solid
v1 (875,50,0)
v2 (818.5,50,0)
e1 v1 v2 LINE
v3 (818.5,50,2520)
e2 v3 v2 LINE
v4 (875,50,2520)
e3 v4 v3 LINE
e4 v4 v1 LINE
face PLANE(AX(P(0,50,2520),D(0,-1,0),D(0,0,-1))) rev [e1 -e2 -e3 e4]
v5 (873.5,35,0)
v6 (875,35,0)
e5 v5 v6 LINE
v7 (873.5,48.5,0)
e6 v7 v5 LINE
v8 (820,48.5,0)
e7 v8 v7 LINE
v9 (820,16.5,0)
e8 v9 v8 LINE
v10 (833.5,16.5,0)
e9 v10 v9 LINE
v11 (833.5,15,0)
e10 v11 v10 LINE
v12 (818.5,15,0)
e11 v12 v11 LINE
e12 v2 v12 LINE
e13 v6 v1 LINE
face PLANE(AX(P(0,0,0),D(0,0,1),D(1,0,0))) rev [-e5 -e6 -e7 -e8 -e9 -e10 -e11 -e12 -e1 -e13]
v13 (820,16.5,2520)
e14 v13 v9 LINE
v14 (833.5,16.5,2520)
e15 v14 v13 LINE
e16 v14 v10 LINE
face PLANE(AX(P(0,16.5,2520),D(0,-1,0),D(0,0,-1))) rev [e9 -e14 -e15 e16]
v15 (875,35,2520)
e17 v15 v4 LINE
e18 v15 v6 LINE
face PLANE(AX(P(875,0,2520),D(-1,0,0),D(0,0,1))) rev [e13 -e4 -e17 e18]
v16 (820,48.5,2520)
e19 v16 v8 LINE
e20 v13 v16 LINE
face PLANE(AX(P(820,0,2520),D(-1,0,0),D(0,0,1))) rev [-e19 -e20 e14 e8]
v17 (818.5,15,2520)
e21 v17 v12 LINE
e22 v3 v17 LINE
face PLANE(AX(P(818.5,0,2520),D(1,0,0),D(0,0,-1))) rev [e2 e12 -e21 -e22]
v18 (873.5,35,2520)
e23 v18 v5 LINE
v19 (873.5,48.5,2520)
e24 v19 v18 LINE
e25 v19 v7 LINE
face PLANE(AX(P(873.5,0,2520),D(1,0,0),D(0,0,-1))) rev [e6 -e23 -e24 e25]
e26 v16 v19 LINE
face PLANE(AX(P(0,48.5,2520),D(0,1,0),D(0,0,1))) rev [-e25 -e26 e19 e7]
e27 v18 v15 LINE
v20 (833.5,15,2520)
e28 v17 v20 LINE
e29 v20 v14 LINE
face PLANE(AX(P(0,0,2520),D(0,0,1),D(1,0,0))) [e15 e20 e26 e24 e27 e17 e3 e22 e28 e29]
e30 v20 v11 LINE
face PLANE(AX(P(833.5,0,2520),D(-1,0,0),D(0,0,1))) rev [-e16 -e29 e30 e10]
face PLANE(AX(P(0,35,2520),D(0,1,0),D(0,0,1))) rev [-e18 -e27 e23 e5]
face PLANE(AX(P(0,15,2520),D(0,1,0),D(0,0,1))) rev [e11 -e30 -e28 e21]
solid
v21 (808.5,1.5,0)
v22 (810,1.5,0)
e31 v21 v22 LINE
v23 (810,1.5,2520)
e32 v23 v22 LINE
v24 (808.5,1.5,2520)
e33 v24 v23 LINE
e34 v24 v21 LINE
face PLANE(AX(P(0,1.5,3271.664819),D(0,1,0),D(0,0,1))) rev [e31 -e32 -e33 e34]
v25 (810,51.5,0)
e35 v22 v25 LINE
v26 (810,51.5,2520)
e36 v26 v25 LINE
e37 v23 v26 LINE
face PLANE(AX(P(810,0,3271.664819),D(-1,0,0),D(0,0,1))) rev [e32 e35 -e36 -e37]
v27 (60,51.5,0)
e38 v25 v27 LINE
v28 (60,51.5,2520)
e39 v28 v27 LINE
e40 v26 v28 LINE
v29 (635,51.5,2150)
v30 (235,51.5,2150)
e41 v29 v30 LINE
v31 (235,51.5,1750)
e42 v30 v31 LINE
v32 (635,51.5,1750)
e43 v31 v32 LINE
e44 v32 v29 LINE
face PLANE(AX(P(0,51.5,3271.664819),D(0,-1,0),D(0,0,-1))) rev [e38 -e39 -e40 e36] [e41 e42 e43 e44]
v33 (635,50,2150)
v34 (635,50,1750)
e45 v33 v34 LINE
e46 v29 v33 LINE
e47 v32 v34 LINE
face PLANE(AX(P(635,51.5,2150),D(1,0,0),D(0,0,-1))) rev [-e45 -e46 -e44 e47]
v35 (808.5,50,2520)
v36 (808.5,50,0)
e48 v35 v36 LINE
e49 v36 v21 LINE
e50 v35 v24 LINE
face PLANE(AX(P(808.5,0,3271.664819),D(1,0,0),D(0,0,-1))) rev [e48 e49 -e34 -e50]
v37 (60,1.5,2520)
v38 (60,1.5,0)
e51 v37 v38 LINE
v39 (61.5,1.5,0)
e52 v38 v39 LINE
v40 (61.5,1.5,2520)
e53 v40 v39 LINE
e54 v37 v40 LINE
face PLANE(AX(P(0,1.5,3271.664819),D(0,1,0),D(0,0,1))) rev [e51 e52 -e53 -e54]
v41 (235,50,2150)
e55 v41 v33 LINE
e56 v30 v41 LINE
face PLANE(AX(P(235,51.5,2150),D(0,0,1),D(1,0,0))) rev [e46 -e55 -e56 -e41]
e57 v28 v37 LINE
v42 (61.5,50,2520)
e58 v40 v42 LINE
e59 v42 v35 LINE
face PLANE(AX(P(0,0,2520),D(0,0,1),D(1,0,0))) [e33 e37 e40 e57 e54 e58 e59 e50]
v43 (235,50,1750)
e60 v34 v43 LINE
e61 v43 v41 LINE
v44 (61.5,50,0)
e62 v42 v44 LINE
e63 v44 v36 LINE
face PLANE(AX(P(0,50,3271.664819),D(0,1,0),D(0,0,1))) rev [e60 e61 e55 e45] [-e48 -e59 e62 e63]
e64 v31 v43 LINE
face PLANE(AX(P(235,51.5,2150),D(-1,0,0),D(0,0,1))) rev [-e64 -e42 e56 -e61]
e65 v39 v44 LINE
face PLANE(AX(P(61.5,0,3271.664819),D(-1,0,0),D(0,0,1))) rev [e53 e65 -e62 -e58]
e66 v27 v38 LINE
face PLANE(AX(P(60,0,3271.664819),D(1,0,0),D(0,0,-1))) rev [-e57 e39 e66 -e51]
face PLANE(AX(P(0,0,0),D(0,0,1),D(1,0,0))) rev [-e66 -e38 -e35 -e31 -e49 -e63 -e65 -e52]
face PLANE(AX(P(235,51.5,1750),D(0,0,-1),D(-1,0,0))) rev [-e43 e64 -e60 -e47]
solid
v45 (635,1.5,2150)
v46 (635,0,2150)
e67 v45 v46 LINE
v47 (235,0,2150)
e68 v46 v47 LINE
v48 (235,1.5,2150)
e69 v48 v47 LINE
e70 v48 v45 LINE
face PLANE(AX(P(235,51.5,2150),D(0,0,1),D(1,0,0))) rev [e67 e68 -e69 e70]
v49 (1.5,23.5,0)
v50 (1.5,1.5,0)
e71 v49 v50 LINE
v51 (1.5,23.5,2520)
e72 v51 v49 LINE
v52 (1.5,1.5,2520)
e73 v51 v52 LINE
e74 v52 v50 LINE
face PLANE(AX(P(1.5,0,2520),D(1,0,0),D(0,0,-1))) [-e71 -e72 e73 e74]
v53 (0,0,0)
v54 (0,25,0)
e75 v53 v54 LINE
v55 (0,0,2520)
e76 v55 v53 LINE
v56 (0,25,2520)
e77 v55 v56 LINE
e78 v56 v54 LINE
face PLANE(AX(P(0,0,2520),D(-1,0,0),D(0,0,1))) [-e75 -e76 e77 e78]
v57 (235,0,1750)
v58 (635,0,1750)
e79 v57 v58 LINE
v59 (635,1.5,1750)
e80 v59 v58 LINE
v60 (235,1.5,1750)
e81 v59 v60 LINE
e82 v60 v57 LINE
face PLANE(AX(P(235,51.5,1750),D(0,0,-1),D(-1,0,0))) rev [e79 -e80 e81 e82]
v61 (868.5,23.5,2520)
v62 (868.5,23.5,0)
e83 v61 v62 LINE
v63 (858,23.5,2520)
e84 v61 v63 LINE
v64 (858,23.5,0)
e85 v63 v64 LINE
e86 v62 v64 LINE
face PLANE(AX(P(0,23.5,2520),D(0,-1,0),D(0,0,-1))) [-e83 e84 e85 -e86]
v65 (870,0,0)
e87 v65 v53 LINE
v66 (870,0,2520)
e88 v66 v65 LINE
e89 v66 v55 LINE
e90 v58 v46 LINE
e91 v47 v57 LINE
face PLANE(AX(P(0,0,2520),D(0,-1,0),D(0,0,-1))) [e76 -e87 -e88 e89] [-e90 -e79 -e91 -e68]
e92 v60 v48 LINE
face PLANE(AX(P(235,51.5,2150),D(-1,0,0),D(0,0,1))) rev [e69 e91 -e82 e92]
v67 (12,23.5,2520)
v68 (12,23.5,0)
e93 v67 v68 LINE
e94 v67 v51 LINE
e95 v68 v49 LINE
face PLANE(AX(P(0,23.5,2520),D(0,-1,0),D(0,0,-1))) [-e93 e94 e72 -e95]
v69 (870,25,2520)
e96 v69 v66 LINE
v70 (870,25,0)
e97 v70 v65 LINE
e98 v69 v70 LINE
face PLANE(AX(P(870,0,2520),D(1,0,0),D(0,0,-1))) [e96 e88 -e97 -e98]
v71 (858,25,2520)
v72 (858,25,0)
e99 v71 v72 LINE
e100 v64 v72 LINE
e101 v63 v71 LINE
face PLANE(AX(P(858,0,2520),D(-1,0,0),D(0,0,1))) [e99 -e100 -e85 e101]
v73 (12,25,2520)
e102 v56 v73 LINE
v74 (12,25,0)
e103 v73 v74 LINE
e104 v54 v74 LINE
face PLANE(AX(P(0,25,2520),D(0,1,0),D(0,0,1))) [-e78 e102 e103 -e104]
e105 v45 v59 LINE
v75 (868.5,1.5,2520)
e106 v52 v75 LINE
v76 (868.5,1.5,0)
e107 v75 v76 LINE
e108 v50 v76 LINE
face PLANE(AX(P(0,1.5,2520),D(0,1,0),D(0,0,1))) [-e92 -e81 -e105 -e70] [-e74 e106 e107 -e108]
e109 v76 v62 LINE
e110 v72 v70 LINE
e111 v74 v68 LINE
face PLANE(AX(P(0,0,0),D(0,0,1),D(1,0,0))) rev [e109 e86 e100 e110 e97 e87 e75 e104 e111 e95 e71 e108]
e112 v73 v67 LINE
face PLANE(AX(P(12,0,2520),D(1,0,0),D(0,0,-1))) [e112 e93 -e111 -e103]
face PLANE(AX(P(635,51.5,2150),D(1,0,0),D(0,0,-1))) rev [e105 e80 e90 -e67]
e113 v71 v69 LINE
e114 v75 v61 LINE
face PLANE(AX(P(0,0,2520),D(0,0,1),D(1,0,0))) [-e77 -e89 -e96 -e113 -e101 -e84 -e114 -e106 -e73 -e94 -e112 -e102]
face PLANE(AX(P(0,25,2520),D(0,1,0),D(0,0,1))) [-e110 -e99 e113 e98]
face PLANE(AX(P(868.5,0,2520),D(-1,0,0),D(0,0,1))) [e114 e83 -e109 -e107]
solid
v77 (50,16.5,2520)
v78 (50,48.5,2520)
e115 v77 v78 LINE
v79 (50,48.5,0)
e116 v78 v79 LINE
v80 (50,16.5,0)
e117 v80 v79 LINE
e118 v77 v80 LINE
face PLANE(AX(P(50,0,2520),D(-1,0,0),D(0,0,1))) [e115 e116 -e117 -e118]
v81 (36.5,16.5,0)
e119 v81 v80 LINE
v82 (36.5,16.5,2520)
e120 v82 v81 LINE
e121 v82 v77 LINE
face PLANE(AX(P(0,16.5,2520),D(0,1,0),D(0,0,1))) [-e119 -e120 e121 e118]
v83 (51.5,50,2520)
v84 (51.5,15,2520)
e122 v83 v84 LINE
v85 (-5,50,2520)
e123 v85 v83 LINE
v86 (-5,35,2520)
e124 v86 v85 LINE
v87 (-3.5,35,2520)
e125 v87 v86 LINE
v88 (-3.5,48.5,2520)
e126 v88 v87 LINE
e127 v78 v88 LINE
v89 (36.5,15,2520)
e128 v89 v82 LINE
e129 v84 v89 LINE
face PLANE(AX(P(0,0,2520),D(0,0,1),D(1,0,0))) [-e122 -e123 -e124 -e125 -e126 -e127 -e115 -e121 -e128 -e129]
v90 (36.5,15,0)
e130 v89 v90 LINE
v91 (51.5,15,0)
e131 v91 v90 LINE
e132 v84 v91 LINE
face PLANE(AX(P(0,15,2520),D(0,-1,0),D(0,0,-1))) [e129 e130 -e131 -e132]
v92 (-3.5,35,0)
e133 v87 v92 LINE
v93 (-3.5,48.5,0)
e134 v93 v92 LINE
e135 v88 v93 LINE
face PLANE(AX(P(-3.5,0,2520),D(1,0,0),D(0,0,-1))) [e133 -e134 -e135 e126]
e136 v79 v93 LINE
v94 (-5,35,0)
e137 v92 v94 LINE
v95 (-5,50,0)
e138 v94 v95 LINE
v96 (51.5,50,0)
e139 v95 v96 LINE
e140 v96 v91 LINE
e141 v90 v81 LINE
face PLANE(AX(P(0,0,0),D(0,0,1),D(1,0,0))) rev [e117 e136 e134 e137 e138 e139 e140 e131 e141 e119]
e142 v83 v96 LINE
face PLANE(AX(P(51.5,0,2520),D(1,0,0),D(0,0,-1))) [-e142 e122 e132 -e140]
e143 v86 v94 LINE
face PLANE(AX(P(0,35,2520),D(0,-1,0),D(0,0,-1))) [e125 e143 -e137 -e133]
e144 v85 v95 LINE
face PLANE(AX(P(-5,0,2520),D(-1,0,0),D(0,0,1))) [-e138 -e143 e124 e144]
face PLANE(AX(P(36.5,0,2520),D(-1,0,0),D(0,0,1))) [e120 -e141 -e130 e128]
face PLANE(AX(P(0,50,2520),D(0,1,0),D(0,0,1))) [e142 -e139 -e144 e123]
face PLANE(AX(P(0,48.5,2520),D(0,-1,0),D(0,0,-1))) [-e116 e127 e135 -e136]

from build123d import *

# Parameters (mm, degrees)
BOSS_EXTRUDE1_DEPTH   = 2520
BOSS_EXTRUDE1_2_DEPTH = 2520
BOSS_EXTRUDE1_3_DEPTH = 2520
BOSS_EXTRUDE2_DEPTH   = 2520
SKETCH2_W             = 400
SKETCH2_H             = 400
CUT_EXTRUDE1_DEPTH    = 2669.084940552


with BuildPart() as part:
    # Sketch 1_3 → Boss-Extrude1 (new body)
    with BuildSketch(Plane.XY):
        Polygon((820, 48.5), (873.5, 48.5), (873.5, 35), (875, 35), (875, 50), (818.5, 50), (818.5, 15), (833.5, 15), (833.5, 16.5), (820, 16.5), align=None)
    extrude(amount=BOSS_EXTRUDE1_DEPTH)


with BuildPart() as body_2:
    # Sketch 1_3 → Boss-Extrude1 2 (new body)
    with BuildSketch(Plane.XY):
        Polygon((-3.5, 48.5), (-3.5, 35), (-5, 35), (-5, 50), (51.5, 50), (51.5, 15), (36.5, 15), (36.5, 16.5), (50, 16.5), (50, 48.5), align=None)
    extrude(amount=BOSS_EXTRUDE1_2_DEPTH)


with BuildPart() as body_3:
    # Sketch 1_3 → Boss-Extrude1 3 (new body)
    with BuildSketch(Plane.XY):
        Polygon((61.5, 1.5), (61.5, 50), (808.5, 50), (808.5, 1.5), (810, 1.5), (810, 51.5), (60, 51.5), (60, 1.5), align=None)
    extrude(amount=BOSS_EXTRUDE1_3_DEPTH)


with BuildPart() as body_4:
    # Sketch 1_3 2 → Boss-Extrude2 (new body)
    with BuildSketch(Plane.XY):
        Polygon((1.5, 23.5), (12, 23.5), (12, 25), (0, 25), (0, 0), (870, 0), (870, 25), (858, 25), (858, 23.5), (868.5, 23.5), (868.5, 1.5), (810, 1.5), (808.5, 1.5), (61.5, 1.5), (60, 1.5), (1.5, 1.5), align=None)
    extrude(amount=BOSS_EXTRUDE2_DEPTH)


with BuildPart() as cut_extrude1_tool:
    # Sketch2 → Cut-Extrude1 (new, through all)
    with BuildSketch(Plane.XZ):
        with Locations((435, 1950)):
            Rectangle(SKETCH2_W, SKETCH2_H)
    extrude(amount=-CUT_EXTRUDE1_DEPTH)


with BuildPart() as body_3_1:
    add(body_3.part)

    # Cut-Extrude1: cut by cut_extrude1_tool
    add(cut_extrude1_tool.part, mode=Mode.SUBTRACT)


with BuildPart() as body_4_1:
    add(body_4.part)

    # Cut-Extrude1: cut by cut_extrude1_tool
    add(cut_extrude1_tool.part, mode=Mode.SUBTRACT)


solid = Compound([part.part, body_2.part, body_3_1.part, body_4_1.part])
